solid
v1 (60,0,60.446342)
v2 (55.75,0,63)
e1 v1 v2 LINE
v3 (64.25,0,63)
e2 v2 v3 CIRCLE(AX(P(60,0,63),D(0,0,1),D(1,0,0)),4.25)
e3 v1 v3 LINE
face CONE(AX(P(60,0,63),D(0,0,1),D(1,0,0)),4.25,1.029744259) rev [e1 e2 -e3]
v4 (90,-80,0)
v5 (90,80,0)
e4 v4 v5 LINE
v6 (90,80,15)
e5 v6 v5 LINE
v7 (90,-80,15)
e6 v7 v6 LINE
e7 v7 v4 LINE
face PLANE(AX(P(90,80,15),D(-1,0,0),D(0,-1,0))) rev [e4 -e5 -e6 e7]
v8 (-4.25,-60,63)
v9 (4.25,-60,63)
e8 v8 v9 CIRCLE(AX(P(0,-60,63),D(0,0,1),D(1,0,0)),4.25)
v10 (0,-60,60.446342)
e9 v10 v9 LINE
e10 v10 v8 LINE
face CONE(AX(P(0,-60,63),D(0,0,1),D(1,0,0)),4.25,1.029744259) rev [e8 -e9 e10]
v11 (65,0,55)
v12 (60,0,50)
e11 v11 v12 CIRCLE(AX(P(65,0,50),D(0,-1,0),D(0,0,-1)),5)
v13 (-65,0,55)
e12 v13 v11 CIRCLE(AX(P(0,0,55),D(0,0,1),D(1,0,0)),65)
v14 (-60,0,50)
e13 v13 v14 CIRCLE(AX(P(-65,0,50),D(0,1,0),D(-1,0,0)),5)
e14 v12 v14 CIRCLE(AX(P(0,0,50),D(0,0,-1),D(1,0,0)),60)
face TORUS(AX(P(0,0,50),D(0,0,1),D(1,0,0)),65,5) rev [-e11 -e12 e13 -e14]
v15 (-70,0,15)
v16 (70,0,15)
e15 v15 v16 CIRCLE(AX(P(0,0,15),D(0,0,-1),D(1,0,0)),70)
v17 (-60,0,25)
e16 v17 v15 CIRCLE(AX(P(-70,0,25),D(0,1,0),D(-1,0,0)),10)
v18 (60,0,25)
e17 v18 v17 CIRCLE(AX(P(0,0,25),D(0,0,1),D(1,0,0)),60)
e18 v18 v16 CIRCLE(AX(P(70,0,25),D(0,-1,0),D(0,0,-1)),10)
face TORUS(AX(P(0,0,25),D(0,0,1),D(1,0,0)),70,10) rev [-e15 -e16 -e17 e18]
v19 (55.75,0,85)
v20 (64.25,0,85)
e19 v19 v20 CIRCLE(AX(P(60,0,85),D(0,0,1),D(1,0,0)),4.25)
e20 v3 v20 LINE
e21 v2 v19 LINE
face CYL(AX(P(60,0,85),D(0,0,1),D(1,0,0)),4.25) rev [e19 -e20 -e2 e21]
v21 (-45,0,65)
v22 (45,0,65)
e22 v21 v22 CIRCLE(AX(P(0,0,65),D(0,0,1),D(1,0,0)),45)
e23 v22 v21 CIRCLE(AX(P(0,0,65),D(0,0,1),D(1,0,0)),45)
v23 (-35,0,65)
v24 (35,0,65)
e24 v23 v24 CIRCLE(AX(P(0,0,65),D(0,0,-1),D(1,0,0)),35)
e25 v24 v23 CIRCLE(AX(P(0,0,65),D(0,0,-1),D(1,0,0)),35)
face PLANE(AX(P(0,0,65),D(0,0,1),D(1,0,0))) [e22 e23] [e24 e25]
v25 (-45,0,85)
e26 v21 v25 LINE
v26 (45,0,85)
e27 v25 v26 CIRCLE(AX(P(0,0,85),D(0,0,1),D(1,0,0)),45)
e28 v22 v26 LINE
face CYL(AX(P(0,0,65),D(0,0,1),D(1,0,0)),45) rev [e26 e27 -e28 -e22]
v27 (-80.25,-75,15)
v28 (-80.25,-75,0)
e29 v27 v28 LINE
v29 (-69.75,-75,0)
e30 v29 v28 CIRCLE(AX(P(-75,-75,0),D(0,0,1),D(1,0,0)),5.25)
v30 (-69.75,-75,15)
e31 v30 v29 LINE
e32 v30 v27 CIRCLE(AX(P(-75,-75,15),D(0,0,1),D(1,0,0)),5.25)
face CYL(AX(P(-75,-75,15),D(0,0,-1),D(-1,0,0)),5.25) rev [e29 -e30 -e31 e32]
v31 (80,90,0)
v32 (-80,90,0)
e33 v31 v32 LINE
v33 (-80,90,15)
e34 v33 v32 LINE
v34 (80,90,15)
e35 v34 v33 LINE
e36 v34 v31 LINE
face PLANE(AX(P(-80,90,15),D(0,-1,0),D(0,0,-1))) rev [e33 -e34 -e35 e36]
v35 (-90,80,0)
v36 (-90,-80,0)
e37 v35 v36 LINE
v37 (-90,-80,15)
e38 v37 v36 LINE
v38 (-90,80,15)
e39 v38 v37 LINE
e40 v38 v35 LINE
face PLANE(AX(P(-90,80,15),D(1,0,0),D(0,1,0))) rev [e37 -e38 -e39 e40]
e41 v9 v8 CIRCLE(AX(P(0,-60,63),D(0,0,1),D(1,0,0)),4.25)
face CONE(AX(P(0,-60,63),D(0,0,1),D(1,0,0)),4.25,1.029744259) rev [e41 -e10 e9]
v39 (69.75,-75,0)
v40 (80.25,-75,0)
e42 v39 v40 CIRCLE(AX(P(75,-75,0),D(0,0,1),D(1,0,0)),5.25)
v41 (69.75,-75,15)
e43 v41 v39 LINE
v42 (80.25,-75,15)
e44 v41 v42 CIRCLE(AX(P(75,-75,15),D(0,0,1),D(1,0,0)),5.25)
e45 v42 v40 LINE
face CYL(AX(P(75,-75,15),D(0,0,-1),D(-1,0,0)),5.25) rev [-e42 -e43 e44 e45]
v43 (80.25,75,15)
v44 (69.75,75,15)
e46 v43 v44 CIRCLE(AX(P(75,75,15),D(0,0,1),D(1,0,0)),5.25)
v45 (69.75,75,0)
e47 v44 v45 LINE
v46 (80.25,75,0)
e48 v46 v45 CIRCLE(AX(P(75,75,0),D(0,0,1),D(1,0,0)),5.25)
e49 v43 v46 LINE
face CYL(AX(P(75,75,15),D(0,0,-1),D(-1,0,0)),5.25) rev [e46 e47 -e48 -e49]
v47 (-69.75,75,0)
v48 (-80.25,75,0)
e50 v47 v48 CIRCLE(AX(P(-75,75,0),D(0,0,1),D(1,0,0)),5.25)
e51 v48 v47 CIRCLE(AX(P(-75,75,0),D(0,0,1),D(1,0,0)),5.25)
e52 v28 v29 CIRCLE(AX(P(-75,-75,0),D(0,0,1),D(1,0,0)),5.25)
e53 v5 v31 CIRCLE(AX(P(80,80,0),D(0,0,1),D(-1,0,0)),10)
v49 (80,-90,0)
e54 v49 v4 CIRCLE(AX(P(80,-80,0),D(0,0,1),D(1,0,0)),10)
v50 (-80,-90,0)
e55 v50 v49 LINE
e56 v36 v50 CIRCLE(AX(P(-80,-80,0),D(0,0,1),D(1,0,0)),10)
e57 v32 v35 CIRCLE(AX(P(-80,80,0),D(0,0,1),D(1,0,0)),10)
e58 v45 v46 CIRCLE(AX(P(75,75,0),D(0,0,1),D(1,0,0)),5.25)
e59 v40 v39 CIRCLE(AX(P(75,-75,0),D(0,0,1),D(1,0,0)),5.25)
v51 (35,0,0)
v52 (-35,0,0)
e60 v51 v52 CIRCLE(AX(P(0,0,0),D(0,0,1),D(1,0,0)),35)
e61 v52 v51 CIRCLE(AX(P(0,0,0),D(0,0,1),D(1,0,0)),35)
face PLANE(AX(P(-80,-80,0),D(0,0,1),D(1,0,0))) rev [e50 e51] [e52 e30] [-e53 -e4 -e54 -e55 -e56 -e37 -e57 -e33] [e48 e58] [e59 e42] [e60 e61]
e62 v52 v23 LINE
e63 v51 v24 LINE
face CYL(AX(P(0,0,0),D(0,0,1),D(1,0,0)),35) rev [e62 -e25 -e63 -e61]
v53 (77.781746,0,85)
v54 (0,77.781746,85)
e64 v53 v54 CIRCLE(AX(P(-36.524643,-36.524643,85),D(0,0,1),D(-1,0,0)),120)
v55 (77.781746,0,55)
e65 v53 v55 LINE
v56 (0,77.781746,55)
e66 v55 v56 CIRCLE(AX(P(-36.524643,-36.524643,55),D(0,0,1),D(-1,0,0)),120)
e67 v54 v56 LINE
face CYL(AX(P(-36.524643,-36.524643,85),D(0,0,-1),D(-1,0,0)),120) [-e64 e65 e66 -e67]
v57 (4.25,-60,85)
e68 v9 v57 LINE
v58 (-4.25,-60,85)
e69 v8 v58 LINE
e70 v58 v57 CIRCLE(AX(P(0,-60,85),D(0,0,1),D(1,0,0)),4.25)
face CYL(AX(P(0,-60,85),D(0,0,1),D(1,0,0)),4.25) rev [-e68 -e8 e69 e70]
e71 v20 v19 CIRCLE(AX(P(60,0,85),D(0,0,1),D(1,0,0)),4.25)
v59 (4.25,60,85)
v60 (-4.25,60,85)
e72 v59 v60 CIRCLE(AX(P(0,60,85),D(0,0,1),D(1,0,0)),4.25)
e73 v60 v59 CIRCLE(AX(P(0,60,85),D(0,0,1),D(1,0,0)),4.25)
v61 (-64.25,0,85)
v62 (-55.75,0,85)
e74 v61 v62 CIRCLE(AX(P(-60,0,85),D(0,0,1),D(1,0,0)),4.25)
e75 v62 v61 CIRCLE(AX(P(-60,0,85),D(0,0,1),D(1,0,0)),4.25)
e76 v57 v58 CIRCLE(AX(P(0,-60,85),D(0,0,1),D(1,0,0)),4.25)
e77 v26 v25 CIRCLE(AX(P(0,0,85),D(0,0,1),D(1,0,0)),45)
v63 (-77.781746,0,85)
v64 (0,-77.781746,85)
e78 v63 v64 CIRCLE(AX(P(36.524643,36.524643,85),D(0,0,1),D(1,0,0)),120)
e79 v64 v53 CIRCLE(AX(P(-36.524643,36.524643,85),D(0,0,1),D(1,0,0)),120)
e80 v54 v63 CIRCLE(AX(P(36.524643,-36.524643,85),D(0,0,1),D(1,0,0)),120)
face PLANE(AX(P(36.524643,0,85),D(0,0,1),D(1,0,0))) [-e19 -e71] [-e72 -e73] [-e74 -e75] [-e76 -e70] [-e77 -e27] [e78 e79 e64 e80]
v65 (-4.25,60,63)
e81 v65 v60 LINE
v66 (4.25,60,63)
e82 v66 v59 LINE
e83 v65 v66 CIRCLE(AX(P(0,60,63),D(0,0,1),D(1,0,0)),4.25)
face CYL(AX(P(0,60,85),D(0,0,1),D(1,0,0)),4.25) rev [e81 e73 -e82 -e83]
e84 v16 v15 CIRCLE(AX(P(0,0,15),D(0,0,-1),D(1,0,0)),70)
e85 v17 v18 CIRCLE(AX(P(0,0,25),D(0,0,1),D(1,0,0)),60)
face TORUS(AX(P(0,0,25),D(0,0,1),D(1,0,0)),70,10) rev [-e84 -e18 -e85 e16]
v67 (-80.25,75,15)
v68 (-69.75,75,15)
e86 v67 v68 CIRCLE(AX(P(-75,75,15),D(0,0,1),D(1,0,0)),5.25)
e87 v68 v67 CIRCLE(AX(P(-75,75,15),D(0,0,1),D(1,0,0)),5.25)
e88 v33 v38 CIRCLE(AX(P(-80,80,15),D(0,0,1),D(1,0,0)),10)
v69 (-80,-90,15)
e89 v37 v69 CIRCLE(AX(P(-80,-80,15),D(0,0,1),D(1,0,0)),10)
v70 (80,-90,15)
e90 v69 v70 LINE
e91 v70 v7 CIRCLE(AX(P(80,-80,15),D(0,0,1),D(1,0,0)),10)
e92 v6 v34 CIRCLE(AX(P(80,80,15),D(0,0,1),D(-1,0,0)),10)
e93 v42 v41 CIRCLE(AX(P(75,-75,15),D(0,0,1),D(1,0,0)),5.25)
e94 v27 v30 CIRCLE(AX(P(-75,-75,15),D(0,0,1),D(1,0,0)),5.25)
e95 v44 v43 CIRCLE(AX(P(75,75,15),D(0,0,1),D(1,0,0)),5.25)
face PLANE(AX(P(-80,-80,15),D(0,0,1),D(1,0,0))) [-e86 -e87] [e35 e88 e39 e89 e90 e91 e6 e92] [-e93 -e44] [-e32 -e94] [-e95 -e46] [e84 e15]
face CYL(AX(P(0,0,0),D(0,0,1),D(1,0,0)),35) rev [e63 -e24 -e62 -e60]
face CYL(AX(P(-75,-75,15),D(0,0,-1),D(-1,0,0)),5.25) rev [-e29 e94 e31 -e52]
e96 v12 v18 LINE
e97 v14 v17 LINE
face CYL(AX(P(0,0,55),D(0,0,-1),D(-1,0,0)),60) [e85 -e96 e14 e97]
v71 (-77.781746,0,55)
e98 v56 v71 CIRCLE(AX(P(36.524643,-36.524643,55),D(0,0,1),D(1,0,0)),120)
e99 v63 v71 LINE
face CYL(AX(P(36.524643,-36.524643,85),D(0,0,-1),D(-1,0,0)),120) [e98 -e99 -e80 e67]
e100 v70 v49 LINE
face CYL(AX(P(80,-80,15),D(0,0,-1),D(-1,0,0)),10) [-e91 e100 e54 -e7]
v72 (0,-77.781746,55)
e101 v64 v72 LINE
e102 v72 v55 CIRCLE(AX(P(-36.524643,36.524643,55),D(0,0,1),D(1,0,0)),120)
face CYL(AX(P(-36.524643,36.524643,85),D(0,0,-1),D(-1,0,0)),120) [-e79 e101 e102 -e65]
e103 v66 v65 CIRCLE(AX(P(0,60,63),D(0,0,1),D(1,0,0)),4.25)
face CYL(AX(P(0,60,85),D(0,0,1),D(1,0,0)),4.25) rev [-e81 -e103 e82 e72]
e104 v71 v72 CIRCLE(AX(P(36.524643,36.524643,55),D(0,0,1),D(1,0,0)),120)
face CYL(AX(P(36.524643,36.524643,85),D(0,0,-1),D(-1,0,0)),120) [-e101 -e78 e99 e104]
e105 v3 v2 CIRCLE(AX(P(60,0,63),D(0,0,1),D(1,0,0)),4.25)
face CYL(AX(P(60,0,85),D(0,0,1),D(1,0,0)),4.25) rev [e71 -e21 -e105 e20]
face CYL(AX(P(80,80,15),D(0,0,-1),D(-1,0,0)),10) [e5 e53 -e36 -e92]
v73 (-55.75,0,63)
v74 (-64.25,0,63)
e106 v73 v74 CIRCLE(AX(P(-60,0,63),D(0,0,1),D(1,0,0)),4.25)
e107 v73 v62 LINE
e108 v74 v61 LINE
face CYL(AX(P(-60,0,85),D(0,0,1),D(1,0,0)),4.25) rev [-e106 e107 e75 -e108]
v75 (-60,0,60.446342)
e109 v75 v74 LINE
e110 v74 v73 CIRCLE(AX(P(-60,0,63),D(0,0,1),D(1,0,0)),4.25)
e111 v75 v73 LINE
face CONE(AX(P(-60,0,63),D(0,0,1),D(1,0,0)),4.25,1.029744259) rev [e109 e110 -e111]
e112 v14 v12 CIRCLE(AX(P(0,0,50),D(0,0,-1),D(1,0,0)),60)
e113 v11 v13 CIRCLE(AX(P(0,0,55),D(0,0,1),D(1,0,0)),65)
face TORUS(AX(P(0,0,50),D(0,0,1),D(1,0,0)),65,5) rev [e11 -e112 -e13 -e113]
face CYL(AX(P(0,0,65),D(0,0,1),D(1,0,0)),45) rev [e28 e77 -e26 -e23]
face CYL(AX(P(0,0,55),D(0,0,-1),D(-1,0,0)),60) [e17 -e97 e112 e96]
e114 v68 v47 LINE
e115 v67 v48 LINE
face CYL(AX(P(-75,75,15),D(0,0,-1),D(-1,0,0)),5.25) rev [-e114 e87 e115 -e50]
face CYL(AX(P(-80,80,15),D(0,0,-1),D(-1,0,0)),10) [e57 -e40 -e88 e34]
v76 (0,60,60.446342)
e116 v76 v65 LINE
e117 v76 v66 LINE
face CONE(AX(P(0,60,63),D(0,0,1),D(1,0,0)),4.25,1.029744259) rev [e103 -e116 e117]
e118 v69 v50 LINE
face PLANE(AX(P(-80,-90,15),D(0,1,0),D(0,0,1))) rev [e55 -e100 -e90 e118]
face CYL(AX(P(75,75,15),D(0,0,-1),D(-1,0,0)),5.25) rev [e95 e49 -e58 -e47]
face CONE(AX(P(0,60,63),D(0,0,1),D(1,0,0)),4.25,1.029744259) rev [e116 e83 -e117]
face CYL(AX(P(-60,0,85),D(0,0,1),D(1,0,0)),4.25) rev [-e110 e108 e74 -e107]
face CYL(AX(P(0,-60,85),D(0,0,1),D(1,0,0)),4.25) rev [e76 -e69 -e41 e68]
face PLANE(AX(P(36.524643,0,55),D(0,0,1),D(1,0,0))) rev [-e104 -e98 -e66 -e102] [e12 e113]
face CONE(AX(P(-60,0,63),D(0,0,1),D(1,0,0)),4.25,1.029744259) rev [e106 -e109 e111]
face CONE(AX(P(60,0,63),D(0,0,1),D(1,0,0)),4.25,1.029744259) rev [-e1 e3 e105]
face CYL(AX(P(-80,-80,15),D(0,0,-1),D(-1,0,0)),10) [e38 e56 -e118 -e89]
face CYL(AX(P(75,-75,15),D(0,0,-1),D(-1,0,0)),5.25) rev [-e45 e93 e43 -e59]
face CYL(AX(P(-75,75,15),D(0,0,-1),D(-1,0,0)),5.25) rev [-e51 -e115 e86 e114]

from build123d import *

# Parameters (mm, degrees)
SKETCH_1_R               = 5.25
EXTRUDE_1_DEPTH          = 15
SKETCH_2_R               = 60
EXTRUDE_2_DEPTH          = 40
EXTRUDE_3_DEPTH          = 30
PATTERN_CIRCULAR_1_COUNT = 4
FILLET_1_R               = 10
FILLET_2_R               = 5
SKETCH_6_R               = 35
CUT_EXTRUDE_1_DEPTH      = 154.05227865
SKETCH_7_R               = 45
CUT_EXTRUDE_2_DEPTH      = 20


with BuildPart() as part:
    # 草图1 → 凸台-拉伸1 (new body)
    with BuildSketch(Plane.XY):
        with BuildLine():
            Line((-80, 90), (80, 90))
            ThreePointArc((80, 90), (87.071067812, 87.071067812), (90, 80))
            Line((90, 80), (90, -80))
            ThreePointArc((90, -80), (87.071067812, -87.071067812), (80, -90))
            Line((80, -90), (-80, -90))
            ThreePointArc((-80, -90), (-87.071067812, -87.071067812), (-90, -80))
            Line((-90, -80), (-90, 80))
            ThreePointArc((-90, 80), (-87.071067812, 87.071067812), (-80, 90))
        make_face()
        with Locations((-75, 75)):
            Circle(SKETCH_1_R, mode=Mode.SUBTRACT)
        with Locations((75, 75)):
            Circle(SKETCH_1_R, mode=Mode.SUBTRACT)
        with Locations((-75, -75)):
            Circle(SKETCH_1_R, mode=Mode.SUBTRACT)
        with Locations((75, -75)):
            Circle(SKETCH_1_R, mode=Mode.SUBTRACT)
    extrude(amount=EXTRUDE_1_DEPTH)

    # 草图2 → 凸台-拉伸2 (add)
    with BuildSketch(Plane.XY.offset(15)):
        Circle(SKETCH_2_R)
    extrude(amount=EXTRUDE_2_DEPTH)

    # 草图3 → 凸台-拉伸3 (add)
    with BuildSketch(Plane.XY.offset(55)):
        with BuildLine():
            ThreePointArc((0, 77.781745931), (48.328171063, 48.328171063), (77.781745931, 0))
            ThreePointArc((77.781745931, 0), (48.328171063, -48.328171063), (0, -77.781745931))
            ThreePointArc((0, -77.781745931), (-48.328171063, -48.328171063), (-77.781745931, 0))
            ThreePointArc((-77.781745931, 0), (-48.328171063, 48.328171063), (0, 77.781745931))
        make_face()
    extrude(amount=EXTRUDE_3_DEPTH)

    # 草图5 → M10 螺纹孔1 (revolve, cut)
    with BuildSketch(Plane(origin=(0, 60, 85), x_dir=(0, -1, 0), z_dir=(1, 0, 0))):
        Polygon((0, 0), (0, 24.553657631), (4.25, 22), (4.25, 0), align=None)
    hole_wizard_m10_1 = revolve(axis=Axis((0, 60, 91.35), (0, 0, -1)), mode=Mode.SUBTRACT)

    # 阵列(圆周)1: M10 螺纹孔1 ×4 about axis
    pattern_circular_1_axis = Axis((0, 0, 0), (0, 0, 1))
    for i in range(1, PATTERN_CIRCULAR_1_COUNT):
        add(hole_wizard_m10_1.rotate(pattern_circular_1_axis, i * 360 / PATTERN_CIRCULAR_1_COUNT), mode=Mode.SUBTRACT)

    # 圆角1
    fillet_1_edges = [part.edges().sort_by_distance(p)[0] for p in [
        (-60, 0, 15),
    ]]
    fillet(fillet_1_edges, radius=FILLET_1_R)

    # 圆角2
    fillet_2_edges = [part.edges().sort_by_distance(p)[0] for p in [
        (-60, 0, 55),
    ]]
    fillet(fillet_2_edges, radius=FILLET_2_R)

    # 草图6 → 切除-拉伸1 (cut, through all)
    with BuildSketch(Plane.XY.offset(85)):
        Circle(SKETCH_6_R)
    extrude(amount=-CUT_EXTRUDE_1_DEPTH, mode=Mode.SUBTRACT)

    # 草图7 → 切除-拉伸2 (cut)
    with BuildSketch(Plane.XY.offset(85)):
        Circle(SKETCH_7_R)
    extrude(amount=-CUT_EXTRUDE_2_DEPTH, mode=Mode.SUBTRACT)


solid = part.part
